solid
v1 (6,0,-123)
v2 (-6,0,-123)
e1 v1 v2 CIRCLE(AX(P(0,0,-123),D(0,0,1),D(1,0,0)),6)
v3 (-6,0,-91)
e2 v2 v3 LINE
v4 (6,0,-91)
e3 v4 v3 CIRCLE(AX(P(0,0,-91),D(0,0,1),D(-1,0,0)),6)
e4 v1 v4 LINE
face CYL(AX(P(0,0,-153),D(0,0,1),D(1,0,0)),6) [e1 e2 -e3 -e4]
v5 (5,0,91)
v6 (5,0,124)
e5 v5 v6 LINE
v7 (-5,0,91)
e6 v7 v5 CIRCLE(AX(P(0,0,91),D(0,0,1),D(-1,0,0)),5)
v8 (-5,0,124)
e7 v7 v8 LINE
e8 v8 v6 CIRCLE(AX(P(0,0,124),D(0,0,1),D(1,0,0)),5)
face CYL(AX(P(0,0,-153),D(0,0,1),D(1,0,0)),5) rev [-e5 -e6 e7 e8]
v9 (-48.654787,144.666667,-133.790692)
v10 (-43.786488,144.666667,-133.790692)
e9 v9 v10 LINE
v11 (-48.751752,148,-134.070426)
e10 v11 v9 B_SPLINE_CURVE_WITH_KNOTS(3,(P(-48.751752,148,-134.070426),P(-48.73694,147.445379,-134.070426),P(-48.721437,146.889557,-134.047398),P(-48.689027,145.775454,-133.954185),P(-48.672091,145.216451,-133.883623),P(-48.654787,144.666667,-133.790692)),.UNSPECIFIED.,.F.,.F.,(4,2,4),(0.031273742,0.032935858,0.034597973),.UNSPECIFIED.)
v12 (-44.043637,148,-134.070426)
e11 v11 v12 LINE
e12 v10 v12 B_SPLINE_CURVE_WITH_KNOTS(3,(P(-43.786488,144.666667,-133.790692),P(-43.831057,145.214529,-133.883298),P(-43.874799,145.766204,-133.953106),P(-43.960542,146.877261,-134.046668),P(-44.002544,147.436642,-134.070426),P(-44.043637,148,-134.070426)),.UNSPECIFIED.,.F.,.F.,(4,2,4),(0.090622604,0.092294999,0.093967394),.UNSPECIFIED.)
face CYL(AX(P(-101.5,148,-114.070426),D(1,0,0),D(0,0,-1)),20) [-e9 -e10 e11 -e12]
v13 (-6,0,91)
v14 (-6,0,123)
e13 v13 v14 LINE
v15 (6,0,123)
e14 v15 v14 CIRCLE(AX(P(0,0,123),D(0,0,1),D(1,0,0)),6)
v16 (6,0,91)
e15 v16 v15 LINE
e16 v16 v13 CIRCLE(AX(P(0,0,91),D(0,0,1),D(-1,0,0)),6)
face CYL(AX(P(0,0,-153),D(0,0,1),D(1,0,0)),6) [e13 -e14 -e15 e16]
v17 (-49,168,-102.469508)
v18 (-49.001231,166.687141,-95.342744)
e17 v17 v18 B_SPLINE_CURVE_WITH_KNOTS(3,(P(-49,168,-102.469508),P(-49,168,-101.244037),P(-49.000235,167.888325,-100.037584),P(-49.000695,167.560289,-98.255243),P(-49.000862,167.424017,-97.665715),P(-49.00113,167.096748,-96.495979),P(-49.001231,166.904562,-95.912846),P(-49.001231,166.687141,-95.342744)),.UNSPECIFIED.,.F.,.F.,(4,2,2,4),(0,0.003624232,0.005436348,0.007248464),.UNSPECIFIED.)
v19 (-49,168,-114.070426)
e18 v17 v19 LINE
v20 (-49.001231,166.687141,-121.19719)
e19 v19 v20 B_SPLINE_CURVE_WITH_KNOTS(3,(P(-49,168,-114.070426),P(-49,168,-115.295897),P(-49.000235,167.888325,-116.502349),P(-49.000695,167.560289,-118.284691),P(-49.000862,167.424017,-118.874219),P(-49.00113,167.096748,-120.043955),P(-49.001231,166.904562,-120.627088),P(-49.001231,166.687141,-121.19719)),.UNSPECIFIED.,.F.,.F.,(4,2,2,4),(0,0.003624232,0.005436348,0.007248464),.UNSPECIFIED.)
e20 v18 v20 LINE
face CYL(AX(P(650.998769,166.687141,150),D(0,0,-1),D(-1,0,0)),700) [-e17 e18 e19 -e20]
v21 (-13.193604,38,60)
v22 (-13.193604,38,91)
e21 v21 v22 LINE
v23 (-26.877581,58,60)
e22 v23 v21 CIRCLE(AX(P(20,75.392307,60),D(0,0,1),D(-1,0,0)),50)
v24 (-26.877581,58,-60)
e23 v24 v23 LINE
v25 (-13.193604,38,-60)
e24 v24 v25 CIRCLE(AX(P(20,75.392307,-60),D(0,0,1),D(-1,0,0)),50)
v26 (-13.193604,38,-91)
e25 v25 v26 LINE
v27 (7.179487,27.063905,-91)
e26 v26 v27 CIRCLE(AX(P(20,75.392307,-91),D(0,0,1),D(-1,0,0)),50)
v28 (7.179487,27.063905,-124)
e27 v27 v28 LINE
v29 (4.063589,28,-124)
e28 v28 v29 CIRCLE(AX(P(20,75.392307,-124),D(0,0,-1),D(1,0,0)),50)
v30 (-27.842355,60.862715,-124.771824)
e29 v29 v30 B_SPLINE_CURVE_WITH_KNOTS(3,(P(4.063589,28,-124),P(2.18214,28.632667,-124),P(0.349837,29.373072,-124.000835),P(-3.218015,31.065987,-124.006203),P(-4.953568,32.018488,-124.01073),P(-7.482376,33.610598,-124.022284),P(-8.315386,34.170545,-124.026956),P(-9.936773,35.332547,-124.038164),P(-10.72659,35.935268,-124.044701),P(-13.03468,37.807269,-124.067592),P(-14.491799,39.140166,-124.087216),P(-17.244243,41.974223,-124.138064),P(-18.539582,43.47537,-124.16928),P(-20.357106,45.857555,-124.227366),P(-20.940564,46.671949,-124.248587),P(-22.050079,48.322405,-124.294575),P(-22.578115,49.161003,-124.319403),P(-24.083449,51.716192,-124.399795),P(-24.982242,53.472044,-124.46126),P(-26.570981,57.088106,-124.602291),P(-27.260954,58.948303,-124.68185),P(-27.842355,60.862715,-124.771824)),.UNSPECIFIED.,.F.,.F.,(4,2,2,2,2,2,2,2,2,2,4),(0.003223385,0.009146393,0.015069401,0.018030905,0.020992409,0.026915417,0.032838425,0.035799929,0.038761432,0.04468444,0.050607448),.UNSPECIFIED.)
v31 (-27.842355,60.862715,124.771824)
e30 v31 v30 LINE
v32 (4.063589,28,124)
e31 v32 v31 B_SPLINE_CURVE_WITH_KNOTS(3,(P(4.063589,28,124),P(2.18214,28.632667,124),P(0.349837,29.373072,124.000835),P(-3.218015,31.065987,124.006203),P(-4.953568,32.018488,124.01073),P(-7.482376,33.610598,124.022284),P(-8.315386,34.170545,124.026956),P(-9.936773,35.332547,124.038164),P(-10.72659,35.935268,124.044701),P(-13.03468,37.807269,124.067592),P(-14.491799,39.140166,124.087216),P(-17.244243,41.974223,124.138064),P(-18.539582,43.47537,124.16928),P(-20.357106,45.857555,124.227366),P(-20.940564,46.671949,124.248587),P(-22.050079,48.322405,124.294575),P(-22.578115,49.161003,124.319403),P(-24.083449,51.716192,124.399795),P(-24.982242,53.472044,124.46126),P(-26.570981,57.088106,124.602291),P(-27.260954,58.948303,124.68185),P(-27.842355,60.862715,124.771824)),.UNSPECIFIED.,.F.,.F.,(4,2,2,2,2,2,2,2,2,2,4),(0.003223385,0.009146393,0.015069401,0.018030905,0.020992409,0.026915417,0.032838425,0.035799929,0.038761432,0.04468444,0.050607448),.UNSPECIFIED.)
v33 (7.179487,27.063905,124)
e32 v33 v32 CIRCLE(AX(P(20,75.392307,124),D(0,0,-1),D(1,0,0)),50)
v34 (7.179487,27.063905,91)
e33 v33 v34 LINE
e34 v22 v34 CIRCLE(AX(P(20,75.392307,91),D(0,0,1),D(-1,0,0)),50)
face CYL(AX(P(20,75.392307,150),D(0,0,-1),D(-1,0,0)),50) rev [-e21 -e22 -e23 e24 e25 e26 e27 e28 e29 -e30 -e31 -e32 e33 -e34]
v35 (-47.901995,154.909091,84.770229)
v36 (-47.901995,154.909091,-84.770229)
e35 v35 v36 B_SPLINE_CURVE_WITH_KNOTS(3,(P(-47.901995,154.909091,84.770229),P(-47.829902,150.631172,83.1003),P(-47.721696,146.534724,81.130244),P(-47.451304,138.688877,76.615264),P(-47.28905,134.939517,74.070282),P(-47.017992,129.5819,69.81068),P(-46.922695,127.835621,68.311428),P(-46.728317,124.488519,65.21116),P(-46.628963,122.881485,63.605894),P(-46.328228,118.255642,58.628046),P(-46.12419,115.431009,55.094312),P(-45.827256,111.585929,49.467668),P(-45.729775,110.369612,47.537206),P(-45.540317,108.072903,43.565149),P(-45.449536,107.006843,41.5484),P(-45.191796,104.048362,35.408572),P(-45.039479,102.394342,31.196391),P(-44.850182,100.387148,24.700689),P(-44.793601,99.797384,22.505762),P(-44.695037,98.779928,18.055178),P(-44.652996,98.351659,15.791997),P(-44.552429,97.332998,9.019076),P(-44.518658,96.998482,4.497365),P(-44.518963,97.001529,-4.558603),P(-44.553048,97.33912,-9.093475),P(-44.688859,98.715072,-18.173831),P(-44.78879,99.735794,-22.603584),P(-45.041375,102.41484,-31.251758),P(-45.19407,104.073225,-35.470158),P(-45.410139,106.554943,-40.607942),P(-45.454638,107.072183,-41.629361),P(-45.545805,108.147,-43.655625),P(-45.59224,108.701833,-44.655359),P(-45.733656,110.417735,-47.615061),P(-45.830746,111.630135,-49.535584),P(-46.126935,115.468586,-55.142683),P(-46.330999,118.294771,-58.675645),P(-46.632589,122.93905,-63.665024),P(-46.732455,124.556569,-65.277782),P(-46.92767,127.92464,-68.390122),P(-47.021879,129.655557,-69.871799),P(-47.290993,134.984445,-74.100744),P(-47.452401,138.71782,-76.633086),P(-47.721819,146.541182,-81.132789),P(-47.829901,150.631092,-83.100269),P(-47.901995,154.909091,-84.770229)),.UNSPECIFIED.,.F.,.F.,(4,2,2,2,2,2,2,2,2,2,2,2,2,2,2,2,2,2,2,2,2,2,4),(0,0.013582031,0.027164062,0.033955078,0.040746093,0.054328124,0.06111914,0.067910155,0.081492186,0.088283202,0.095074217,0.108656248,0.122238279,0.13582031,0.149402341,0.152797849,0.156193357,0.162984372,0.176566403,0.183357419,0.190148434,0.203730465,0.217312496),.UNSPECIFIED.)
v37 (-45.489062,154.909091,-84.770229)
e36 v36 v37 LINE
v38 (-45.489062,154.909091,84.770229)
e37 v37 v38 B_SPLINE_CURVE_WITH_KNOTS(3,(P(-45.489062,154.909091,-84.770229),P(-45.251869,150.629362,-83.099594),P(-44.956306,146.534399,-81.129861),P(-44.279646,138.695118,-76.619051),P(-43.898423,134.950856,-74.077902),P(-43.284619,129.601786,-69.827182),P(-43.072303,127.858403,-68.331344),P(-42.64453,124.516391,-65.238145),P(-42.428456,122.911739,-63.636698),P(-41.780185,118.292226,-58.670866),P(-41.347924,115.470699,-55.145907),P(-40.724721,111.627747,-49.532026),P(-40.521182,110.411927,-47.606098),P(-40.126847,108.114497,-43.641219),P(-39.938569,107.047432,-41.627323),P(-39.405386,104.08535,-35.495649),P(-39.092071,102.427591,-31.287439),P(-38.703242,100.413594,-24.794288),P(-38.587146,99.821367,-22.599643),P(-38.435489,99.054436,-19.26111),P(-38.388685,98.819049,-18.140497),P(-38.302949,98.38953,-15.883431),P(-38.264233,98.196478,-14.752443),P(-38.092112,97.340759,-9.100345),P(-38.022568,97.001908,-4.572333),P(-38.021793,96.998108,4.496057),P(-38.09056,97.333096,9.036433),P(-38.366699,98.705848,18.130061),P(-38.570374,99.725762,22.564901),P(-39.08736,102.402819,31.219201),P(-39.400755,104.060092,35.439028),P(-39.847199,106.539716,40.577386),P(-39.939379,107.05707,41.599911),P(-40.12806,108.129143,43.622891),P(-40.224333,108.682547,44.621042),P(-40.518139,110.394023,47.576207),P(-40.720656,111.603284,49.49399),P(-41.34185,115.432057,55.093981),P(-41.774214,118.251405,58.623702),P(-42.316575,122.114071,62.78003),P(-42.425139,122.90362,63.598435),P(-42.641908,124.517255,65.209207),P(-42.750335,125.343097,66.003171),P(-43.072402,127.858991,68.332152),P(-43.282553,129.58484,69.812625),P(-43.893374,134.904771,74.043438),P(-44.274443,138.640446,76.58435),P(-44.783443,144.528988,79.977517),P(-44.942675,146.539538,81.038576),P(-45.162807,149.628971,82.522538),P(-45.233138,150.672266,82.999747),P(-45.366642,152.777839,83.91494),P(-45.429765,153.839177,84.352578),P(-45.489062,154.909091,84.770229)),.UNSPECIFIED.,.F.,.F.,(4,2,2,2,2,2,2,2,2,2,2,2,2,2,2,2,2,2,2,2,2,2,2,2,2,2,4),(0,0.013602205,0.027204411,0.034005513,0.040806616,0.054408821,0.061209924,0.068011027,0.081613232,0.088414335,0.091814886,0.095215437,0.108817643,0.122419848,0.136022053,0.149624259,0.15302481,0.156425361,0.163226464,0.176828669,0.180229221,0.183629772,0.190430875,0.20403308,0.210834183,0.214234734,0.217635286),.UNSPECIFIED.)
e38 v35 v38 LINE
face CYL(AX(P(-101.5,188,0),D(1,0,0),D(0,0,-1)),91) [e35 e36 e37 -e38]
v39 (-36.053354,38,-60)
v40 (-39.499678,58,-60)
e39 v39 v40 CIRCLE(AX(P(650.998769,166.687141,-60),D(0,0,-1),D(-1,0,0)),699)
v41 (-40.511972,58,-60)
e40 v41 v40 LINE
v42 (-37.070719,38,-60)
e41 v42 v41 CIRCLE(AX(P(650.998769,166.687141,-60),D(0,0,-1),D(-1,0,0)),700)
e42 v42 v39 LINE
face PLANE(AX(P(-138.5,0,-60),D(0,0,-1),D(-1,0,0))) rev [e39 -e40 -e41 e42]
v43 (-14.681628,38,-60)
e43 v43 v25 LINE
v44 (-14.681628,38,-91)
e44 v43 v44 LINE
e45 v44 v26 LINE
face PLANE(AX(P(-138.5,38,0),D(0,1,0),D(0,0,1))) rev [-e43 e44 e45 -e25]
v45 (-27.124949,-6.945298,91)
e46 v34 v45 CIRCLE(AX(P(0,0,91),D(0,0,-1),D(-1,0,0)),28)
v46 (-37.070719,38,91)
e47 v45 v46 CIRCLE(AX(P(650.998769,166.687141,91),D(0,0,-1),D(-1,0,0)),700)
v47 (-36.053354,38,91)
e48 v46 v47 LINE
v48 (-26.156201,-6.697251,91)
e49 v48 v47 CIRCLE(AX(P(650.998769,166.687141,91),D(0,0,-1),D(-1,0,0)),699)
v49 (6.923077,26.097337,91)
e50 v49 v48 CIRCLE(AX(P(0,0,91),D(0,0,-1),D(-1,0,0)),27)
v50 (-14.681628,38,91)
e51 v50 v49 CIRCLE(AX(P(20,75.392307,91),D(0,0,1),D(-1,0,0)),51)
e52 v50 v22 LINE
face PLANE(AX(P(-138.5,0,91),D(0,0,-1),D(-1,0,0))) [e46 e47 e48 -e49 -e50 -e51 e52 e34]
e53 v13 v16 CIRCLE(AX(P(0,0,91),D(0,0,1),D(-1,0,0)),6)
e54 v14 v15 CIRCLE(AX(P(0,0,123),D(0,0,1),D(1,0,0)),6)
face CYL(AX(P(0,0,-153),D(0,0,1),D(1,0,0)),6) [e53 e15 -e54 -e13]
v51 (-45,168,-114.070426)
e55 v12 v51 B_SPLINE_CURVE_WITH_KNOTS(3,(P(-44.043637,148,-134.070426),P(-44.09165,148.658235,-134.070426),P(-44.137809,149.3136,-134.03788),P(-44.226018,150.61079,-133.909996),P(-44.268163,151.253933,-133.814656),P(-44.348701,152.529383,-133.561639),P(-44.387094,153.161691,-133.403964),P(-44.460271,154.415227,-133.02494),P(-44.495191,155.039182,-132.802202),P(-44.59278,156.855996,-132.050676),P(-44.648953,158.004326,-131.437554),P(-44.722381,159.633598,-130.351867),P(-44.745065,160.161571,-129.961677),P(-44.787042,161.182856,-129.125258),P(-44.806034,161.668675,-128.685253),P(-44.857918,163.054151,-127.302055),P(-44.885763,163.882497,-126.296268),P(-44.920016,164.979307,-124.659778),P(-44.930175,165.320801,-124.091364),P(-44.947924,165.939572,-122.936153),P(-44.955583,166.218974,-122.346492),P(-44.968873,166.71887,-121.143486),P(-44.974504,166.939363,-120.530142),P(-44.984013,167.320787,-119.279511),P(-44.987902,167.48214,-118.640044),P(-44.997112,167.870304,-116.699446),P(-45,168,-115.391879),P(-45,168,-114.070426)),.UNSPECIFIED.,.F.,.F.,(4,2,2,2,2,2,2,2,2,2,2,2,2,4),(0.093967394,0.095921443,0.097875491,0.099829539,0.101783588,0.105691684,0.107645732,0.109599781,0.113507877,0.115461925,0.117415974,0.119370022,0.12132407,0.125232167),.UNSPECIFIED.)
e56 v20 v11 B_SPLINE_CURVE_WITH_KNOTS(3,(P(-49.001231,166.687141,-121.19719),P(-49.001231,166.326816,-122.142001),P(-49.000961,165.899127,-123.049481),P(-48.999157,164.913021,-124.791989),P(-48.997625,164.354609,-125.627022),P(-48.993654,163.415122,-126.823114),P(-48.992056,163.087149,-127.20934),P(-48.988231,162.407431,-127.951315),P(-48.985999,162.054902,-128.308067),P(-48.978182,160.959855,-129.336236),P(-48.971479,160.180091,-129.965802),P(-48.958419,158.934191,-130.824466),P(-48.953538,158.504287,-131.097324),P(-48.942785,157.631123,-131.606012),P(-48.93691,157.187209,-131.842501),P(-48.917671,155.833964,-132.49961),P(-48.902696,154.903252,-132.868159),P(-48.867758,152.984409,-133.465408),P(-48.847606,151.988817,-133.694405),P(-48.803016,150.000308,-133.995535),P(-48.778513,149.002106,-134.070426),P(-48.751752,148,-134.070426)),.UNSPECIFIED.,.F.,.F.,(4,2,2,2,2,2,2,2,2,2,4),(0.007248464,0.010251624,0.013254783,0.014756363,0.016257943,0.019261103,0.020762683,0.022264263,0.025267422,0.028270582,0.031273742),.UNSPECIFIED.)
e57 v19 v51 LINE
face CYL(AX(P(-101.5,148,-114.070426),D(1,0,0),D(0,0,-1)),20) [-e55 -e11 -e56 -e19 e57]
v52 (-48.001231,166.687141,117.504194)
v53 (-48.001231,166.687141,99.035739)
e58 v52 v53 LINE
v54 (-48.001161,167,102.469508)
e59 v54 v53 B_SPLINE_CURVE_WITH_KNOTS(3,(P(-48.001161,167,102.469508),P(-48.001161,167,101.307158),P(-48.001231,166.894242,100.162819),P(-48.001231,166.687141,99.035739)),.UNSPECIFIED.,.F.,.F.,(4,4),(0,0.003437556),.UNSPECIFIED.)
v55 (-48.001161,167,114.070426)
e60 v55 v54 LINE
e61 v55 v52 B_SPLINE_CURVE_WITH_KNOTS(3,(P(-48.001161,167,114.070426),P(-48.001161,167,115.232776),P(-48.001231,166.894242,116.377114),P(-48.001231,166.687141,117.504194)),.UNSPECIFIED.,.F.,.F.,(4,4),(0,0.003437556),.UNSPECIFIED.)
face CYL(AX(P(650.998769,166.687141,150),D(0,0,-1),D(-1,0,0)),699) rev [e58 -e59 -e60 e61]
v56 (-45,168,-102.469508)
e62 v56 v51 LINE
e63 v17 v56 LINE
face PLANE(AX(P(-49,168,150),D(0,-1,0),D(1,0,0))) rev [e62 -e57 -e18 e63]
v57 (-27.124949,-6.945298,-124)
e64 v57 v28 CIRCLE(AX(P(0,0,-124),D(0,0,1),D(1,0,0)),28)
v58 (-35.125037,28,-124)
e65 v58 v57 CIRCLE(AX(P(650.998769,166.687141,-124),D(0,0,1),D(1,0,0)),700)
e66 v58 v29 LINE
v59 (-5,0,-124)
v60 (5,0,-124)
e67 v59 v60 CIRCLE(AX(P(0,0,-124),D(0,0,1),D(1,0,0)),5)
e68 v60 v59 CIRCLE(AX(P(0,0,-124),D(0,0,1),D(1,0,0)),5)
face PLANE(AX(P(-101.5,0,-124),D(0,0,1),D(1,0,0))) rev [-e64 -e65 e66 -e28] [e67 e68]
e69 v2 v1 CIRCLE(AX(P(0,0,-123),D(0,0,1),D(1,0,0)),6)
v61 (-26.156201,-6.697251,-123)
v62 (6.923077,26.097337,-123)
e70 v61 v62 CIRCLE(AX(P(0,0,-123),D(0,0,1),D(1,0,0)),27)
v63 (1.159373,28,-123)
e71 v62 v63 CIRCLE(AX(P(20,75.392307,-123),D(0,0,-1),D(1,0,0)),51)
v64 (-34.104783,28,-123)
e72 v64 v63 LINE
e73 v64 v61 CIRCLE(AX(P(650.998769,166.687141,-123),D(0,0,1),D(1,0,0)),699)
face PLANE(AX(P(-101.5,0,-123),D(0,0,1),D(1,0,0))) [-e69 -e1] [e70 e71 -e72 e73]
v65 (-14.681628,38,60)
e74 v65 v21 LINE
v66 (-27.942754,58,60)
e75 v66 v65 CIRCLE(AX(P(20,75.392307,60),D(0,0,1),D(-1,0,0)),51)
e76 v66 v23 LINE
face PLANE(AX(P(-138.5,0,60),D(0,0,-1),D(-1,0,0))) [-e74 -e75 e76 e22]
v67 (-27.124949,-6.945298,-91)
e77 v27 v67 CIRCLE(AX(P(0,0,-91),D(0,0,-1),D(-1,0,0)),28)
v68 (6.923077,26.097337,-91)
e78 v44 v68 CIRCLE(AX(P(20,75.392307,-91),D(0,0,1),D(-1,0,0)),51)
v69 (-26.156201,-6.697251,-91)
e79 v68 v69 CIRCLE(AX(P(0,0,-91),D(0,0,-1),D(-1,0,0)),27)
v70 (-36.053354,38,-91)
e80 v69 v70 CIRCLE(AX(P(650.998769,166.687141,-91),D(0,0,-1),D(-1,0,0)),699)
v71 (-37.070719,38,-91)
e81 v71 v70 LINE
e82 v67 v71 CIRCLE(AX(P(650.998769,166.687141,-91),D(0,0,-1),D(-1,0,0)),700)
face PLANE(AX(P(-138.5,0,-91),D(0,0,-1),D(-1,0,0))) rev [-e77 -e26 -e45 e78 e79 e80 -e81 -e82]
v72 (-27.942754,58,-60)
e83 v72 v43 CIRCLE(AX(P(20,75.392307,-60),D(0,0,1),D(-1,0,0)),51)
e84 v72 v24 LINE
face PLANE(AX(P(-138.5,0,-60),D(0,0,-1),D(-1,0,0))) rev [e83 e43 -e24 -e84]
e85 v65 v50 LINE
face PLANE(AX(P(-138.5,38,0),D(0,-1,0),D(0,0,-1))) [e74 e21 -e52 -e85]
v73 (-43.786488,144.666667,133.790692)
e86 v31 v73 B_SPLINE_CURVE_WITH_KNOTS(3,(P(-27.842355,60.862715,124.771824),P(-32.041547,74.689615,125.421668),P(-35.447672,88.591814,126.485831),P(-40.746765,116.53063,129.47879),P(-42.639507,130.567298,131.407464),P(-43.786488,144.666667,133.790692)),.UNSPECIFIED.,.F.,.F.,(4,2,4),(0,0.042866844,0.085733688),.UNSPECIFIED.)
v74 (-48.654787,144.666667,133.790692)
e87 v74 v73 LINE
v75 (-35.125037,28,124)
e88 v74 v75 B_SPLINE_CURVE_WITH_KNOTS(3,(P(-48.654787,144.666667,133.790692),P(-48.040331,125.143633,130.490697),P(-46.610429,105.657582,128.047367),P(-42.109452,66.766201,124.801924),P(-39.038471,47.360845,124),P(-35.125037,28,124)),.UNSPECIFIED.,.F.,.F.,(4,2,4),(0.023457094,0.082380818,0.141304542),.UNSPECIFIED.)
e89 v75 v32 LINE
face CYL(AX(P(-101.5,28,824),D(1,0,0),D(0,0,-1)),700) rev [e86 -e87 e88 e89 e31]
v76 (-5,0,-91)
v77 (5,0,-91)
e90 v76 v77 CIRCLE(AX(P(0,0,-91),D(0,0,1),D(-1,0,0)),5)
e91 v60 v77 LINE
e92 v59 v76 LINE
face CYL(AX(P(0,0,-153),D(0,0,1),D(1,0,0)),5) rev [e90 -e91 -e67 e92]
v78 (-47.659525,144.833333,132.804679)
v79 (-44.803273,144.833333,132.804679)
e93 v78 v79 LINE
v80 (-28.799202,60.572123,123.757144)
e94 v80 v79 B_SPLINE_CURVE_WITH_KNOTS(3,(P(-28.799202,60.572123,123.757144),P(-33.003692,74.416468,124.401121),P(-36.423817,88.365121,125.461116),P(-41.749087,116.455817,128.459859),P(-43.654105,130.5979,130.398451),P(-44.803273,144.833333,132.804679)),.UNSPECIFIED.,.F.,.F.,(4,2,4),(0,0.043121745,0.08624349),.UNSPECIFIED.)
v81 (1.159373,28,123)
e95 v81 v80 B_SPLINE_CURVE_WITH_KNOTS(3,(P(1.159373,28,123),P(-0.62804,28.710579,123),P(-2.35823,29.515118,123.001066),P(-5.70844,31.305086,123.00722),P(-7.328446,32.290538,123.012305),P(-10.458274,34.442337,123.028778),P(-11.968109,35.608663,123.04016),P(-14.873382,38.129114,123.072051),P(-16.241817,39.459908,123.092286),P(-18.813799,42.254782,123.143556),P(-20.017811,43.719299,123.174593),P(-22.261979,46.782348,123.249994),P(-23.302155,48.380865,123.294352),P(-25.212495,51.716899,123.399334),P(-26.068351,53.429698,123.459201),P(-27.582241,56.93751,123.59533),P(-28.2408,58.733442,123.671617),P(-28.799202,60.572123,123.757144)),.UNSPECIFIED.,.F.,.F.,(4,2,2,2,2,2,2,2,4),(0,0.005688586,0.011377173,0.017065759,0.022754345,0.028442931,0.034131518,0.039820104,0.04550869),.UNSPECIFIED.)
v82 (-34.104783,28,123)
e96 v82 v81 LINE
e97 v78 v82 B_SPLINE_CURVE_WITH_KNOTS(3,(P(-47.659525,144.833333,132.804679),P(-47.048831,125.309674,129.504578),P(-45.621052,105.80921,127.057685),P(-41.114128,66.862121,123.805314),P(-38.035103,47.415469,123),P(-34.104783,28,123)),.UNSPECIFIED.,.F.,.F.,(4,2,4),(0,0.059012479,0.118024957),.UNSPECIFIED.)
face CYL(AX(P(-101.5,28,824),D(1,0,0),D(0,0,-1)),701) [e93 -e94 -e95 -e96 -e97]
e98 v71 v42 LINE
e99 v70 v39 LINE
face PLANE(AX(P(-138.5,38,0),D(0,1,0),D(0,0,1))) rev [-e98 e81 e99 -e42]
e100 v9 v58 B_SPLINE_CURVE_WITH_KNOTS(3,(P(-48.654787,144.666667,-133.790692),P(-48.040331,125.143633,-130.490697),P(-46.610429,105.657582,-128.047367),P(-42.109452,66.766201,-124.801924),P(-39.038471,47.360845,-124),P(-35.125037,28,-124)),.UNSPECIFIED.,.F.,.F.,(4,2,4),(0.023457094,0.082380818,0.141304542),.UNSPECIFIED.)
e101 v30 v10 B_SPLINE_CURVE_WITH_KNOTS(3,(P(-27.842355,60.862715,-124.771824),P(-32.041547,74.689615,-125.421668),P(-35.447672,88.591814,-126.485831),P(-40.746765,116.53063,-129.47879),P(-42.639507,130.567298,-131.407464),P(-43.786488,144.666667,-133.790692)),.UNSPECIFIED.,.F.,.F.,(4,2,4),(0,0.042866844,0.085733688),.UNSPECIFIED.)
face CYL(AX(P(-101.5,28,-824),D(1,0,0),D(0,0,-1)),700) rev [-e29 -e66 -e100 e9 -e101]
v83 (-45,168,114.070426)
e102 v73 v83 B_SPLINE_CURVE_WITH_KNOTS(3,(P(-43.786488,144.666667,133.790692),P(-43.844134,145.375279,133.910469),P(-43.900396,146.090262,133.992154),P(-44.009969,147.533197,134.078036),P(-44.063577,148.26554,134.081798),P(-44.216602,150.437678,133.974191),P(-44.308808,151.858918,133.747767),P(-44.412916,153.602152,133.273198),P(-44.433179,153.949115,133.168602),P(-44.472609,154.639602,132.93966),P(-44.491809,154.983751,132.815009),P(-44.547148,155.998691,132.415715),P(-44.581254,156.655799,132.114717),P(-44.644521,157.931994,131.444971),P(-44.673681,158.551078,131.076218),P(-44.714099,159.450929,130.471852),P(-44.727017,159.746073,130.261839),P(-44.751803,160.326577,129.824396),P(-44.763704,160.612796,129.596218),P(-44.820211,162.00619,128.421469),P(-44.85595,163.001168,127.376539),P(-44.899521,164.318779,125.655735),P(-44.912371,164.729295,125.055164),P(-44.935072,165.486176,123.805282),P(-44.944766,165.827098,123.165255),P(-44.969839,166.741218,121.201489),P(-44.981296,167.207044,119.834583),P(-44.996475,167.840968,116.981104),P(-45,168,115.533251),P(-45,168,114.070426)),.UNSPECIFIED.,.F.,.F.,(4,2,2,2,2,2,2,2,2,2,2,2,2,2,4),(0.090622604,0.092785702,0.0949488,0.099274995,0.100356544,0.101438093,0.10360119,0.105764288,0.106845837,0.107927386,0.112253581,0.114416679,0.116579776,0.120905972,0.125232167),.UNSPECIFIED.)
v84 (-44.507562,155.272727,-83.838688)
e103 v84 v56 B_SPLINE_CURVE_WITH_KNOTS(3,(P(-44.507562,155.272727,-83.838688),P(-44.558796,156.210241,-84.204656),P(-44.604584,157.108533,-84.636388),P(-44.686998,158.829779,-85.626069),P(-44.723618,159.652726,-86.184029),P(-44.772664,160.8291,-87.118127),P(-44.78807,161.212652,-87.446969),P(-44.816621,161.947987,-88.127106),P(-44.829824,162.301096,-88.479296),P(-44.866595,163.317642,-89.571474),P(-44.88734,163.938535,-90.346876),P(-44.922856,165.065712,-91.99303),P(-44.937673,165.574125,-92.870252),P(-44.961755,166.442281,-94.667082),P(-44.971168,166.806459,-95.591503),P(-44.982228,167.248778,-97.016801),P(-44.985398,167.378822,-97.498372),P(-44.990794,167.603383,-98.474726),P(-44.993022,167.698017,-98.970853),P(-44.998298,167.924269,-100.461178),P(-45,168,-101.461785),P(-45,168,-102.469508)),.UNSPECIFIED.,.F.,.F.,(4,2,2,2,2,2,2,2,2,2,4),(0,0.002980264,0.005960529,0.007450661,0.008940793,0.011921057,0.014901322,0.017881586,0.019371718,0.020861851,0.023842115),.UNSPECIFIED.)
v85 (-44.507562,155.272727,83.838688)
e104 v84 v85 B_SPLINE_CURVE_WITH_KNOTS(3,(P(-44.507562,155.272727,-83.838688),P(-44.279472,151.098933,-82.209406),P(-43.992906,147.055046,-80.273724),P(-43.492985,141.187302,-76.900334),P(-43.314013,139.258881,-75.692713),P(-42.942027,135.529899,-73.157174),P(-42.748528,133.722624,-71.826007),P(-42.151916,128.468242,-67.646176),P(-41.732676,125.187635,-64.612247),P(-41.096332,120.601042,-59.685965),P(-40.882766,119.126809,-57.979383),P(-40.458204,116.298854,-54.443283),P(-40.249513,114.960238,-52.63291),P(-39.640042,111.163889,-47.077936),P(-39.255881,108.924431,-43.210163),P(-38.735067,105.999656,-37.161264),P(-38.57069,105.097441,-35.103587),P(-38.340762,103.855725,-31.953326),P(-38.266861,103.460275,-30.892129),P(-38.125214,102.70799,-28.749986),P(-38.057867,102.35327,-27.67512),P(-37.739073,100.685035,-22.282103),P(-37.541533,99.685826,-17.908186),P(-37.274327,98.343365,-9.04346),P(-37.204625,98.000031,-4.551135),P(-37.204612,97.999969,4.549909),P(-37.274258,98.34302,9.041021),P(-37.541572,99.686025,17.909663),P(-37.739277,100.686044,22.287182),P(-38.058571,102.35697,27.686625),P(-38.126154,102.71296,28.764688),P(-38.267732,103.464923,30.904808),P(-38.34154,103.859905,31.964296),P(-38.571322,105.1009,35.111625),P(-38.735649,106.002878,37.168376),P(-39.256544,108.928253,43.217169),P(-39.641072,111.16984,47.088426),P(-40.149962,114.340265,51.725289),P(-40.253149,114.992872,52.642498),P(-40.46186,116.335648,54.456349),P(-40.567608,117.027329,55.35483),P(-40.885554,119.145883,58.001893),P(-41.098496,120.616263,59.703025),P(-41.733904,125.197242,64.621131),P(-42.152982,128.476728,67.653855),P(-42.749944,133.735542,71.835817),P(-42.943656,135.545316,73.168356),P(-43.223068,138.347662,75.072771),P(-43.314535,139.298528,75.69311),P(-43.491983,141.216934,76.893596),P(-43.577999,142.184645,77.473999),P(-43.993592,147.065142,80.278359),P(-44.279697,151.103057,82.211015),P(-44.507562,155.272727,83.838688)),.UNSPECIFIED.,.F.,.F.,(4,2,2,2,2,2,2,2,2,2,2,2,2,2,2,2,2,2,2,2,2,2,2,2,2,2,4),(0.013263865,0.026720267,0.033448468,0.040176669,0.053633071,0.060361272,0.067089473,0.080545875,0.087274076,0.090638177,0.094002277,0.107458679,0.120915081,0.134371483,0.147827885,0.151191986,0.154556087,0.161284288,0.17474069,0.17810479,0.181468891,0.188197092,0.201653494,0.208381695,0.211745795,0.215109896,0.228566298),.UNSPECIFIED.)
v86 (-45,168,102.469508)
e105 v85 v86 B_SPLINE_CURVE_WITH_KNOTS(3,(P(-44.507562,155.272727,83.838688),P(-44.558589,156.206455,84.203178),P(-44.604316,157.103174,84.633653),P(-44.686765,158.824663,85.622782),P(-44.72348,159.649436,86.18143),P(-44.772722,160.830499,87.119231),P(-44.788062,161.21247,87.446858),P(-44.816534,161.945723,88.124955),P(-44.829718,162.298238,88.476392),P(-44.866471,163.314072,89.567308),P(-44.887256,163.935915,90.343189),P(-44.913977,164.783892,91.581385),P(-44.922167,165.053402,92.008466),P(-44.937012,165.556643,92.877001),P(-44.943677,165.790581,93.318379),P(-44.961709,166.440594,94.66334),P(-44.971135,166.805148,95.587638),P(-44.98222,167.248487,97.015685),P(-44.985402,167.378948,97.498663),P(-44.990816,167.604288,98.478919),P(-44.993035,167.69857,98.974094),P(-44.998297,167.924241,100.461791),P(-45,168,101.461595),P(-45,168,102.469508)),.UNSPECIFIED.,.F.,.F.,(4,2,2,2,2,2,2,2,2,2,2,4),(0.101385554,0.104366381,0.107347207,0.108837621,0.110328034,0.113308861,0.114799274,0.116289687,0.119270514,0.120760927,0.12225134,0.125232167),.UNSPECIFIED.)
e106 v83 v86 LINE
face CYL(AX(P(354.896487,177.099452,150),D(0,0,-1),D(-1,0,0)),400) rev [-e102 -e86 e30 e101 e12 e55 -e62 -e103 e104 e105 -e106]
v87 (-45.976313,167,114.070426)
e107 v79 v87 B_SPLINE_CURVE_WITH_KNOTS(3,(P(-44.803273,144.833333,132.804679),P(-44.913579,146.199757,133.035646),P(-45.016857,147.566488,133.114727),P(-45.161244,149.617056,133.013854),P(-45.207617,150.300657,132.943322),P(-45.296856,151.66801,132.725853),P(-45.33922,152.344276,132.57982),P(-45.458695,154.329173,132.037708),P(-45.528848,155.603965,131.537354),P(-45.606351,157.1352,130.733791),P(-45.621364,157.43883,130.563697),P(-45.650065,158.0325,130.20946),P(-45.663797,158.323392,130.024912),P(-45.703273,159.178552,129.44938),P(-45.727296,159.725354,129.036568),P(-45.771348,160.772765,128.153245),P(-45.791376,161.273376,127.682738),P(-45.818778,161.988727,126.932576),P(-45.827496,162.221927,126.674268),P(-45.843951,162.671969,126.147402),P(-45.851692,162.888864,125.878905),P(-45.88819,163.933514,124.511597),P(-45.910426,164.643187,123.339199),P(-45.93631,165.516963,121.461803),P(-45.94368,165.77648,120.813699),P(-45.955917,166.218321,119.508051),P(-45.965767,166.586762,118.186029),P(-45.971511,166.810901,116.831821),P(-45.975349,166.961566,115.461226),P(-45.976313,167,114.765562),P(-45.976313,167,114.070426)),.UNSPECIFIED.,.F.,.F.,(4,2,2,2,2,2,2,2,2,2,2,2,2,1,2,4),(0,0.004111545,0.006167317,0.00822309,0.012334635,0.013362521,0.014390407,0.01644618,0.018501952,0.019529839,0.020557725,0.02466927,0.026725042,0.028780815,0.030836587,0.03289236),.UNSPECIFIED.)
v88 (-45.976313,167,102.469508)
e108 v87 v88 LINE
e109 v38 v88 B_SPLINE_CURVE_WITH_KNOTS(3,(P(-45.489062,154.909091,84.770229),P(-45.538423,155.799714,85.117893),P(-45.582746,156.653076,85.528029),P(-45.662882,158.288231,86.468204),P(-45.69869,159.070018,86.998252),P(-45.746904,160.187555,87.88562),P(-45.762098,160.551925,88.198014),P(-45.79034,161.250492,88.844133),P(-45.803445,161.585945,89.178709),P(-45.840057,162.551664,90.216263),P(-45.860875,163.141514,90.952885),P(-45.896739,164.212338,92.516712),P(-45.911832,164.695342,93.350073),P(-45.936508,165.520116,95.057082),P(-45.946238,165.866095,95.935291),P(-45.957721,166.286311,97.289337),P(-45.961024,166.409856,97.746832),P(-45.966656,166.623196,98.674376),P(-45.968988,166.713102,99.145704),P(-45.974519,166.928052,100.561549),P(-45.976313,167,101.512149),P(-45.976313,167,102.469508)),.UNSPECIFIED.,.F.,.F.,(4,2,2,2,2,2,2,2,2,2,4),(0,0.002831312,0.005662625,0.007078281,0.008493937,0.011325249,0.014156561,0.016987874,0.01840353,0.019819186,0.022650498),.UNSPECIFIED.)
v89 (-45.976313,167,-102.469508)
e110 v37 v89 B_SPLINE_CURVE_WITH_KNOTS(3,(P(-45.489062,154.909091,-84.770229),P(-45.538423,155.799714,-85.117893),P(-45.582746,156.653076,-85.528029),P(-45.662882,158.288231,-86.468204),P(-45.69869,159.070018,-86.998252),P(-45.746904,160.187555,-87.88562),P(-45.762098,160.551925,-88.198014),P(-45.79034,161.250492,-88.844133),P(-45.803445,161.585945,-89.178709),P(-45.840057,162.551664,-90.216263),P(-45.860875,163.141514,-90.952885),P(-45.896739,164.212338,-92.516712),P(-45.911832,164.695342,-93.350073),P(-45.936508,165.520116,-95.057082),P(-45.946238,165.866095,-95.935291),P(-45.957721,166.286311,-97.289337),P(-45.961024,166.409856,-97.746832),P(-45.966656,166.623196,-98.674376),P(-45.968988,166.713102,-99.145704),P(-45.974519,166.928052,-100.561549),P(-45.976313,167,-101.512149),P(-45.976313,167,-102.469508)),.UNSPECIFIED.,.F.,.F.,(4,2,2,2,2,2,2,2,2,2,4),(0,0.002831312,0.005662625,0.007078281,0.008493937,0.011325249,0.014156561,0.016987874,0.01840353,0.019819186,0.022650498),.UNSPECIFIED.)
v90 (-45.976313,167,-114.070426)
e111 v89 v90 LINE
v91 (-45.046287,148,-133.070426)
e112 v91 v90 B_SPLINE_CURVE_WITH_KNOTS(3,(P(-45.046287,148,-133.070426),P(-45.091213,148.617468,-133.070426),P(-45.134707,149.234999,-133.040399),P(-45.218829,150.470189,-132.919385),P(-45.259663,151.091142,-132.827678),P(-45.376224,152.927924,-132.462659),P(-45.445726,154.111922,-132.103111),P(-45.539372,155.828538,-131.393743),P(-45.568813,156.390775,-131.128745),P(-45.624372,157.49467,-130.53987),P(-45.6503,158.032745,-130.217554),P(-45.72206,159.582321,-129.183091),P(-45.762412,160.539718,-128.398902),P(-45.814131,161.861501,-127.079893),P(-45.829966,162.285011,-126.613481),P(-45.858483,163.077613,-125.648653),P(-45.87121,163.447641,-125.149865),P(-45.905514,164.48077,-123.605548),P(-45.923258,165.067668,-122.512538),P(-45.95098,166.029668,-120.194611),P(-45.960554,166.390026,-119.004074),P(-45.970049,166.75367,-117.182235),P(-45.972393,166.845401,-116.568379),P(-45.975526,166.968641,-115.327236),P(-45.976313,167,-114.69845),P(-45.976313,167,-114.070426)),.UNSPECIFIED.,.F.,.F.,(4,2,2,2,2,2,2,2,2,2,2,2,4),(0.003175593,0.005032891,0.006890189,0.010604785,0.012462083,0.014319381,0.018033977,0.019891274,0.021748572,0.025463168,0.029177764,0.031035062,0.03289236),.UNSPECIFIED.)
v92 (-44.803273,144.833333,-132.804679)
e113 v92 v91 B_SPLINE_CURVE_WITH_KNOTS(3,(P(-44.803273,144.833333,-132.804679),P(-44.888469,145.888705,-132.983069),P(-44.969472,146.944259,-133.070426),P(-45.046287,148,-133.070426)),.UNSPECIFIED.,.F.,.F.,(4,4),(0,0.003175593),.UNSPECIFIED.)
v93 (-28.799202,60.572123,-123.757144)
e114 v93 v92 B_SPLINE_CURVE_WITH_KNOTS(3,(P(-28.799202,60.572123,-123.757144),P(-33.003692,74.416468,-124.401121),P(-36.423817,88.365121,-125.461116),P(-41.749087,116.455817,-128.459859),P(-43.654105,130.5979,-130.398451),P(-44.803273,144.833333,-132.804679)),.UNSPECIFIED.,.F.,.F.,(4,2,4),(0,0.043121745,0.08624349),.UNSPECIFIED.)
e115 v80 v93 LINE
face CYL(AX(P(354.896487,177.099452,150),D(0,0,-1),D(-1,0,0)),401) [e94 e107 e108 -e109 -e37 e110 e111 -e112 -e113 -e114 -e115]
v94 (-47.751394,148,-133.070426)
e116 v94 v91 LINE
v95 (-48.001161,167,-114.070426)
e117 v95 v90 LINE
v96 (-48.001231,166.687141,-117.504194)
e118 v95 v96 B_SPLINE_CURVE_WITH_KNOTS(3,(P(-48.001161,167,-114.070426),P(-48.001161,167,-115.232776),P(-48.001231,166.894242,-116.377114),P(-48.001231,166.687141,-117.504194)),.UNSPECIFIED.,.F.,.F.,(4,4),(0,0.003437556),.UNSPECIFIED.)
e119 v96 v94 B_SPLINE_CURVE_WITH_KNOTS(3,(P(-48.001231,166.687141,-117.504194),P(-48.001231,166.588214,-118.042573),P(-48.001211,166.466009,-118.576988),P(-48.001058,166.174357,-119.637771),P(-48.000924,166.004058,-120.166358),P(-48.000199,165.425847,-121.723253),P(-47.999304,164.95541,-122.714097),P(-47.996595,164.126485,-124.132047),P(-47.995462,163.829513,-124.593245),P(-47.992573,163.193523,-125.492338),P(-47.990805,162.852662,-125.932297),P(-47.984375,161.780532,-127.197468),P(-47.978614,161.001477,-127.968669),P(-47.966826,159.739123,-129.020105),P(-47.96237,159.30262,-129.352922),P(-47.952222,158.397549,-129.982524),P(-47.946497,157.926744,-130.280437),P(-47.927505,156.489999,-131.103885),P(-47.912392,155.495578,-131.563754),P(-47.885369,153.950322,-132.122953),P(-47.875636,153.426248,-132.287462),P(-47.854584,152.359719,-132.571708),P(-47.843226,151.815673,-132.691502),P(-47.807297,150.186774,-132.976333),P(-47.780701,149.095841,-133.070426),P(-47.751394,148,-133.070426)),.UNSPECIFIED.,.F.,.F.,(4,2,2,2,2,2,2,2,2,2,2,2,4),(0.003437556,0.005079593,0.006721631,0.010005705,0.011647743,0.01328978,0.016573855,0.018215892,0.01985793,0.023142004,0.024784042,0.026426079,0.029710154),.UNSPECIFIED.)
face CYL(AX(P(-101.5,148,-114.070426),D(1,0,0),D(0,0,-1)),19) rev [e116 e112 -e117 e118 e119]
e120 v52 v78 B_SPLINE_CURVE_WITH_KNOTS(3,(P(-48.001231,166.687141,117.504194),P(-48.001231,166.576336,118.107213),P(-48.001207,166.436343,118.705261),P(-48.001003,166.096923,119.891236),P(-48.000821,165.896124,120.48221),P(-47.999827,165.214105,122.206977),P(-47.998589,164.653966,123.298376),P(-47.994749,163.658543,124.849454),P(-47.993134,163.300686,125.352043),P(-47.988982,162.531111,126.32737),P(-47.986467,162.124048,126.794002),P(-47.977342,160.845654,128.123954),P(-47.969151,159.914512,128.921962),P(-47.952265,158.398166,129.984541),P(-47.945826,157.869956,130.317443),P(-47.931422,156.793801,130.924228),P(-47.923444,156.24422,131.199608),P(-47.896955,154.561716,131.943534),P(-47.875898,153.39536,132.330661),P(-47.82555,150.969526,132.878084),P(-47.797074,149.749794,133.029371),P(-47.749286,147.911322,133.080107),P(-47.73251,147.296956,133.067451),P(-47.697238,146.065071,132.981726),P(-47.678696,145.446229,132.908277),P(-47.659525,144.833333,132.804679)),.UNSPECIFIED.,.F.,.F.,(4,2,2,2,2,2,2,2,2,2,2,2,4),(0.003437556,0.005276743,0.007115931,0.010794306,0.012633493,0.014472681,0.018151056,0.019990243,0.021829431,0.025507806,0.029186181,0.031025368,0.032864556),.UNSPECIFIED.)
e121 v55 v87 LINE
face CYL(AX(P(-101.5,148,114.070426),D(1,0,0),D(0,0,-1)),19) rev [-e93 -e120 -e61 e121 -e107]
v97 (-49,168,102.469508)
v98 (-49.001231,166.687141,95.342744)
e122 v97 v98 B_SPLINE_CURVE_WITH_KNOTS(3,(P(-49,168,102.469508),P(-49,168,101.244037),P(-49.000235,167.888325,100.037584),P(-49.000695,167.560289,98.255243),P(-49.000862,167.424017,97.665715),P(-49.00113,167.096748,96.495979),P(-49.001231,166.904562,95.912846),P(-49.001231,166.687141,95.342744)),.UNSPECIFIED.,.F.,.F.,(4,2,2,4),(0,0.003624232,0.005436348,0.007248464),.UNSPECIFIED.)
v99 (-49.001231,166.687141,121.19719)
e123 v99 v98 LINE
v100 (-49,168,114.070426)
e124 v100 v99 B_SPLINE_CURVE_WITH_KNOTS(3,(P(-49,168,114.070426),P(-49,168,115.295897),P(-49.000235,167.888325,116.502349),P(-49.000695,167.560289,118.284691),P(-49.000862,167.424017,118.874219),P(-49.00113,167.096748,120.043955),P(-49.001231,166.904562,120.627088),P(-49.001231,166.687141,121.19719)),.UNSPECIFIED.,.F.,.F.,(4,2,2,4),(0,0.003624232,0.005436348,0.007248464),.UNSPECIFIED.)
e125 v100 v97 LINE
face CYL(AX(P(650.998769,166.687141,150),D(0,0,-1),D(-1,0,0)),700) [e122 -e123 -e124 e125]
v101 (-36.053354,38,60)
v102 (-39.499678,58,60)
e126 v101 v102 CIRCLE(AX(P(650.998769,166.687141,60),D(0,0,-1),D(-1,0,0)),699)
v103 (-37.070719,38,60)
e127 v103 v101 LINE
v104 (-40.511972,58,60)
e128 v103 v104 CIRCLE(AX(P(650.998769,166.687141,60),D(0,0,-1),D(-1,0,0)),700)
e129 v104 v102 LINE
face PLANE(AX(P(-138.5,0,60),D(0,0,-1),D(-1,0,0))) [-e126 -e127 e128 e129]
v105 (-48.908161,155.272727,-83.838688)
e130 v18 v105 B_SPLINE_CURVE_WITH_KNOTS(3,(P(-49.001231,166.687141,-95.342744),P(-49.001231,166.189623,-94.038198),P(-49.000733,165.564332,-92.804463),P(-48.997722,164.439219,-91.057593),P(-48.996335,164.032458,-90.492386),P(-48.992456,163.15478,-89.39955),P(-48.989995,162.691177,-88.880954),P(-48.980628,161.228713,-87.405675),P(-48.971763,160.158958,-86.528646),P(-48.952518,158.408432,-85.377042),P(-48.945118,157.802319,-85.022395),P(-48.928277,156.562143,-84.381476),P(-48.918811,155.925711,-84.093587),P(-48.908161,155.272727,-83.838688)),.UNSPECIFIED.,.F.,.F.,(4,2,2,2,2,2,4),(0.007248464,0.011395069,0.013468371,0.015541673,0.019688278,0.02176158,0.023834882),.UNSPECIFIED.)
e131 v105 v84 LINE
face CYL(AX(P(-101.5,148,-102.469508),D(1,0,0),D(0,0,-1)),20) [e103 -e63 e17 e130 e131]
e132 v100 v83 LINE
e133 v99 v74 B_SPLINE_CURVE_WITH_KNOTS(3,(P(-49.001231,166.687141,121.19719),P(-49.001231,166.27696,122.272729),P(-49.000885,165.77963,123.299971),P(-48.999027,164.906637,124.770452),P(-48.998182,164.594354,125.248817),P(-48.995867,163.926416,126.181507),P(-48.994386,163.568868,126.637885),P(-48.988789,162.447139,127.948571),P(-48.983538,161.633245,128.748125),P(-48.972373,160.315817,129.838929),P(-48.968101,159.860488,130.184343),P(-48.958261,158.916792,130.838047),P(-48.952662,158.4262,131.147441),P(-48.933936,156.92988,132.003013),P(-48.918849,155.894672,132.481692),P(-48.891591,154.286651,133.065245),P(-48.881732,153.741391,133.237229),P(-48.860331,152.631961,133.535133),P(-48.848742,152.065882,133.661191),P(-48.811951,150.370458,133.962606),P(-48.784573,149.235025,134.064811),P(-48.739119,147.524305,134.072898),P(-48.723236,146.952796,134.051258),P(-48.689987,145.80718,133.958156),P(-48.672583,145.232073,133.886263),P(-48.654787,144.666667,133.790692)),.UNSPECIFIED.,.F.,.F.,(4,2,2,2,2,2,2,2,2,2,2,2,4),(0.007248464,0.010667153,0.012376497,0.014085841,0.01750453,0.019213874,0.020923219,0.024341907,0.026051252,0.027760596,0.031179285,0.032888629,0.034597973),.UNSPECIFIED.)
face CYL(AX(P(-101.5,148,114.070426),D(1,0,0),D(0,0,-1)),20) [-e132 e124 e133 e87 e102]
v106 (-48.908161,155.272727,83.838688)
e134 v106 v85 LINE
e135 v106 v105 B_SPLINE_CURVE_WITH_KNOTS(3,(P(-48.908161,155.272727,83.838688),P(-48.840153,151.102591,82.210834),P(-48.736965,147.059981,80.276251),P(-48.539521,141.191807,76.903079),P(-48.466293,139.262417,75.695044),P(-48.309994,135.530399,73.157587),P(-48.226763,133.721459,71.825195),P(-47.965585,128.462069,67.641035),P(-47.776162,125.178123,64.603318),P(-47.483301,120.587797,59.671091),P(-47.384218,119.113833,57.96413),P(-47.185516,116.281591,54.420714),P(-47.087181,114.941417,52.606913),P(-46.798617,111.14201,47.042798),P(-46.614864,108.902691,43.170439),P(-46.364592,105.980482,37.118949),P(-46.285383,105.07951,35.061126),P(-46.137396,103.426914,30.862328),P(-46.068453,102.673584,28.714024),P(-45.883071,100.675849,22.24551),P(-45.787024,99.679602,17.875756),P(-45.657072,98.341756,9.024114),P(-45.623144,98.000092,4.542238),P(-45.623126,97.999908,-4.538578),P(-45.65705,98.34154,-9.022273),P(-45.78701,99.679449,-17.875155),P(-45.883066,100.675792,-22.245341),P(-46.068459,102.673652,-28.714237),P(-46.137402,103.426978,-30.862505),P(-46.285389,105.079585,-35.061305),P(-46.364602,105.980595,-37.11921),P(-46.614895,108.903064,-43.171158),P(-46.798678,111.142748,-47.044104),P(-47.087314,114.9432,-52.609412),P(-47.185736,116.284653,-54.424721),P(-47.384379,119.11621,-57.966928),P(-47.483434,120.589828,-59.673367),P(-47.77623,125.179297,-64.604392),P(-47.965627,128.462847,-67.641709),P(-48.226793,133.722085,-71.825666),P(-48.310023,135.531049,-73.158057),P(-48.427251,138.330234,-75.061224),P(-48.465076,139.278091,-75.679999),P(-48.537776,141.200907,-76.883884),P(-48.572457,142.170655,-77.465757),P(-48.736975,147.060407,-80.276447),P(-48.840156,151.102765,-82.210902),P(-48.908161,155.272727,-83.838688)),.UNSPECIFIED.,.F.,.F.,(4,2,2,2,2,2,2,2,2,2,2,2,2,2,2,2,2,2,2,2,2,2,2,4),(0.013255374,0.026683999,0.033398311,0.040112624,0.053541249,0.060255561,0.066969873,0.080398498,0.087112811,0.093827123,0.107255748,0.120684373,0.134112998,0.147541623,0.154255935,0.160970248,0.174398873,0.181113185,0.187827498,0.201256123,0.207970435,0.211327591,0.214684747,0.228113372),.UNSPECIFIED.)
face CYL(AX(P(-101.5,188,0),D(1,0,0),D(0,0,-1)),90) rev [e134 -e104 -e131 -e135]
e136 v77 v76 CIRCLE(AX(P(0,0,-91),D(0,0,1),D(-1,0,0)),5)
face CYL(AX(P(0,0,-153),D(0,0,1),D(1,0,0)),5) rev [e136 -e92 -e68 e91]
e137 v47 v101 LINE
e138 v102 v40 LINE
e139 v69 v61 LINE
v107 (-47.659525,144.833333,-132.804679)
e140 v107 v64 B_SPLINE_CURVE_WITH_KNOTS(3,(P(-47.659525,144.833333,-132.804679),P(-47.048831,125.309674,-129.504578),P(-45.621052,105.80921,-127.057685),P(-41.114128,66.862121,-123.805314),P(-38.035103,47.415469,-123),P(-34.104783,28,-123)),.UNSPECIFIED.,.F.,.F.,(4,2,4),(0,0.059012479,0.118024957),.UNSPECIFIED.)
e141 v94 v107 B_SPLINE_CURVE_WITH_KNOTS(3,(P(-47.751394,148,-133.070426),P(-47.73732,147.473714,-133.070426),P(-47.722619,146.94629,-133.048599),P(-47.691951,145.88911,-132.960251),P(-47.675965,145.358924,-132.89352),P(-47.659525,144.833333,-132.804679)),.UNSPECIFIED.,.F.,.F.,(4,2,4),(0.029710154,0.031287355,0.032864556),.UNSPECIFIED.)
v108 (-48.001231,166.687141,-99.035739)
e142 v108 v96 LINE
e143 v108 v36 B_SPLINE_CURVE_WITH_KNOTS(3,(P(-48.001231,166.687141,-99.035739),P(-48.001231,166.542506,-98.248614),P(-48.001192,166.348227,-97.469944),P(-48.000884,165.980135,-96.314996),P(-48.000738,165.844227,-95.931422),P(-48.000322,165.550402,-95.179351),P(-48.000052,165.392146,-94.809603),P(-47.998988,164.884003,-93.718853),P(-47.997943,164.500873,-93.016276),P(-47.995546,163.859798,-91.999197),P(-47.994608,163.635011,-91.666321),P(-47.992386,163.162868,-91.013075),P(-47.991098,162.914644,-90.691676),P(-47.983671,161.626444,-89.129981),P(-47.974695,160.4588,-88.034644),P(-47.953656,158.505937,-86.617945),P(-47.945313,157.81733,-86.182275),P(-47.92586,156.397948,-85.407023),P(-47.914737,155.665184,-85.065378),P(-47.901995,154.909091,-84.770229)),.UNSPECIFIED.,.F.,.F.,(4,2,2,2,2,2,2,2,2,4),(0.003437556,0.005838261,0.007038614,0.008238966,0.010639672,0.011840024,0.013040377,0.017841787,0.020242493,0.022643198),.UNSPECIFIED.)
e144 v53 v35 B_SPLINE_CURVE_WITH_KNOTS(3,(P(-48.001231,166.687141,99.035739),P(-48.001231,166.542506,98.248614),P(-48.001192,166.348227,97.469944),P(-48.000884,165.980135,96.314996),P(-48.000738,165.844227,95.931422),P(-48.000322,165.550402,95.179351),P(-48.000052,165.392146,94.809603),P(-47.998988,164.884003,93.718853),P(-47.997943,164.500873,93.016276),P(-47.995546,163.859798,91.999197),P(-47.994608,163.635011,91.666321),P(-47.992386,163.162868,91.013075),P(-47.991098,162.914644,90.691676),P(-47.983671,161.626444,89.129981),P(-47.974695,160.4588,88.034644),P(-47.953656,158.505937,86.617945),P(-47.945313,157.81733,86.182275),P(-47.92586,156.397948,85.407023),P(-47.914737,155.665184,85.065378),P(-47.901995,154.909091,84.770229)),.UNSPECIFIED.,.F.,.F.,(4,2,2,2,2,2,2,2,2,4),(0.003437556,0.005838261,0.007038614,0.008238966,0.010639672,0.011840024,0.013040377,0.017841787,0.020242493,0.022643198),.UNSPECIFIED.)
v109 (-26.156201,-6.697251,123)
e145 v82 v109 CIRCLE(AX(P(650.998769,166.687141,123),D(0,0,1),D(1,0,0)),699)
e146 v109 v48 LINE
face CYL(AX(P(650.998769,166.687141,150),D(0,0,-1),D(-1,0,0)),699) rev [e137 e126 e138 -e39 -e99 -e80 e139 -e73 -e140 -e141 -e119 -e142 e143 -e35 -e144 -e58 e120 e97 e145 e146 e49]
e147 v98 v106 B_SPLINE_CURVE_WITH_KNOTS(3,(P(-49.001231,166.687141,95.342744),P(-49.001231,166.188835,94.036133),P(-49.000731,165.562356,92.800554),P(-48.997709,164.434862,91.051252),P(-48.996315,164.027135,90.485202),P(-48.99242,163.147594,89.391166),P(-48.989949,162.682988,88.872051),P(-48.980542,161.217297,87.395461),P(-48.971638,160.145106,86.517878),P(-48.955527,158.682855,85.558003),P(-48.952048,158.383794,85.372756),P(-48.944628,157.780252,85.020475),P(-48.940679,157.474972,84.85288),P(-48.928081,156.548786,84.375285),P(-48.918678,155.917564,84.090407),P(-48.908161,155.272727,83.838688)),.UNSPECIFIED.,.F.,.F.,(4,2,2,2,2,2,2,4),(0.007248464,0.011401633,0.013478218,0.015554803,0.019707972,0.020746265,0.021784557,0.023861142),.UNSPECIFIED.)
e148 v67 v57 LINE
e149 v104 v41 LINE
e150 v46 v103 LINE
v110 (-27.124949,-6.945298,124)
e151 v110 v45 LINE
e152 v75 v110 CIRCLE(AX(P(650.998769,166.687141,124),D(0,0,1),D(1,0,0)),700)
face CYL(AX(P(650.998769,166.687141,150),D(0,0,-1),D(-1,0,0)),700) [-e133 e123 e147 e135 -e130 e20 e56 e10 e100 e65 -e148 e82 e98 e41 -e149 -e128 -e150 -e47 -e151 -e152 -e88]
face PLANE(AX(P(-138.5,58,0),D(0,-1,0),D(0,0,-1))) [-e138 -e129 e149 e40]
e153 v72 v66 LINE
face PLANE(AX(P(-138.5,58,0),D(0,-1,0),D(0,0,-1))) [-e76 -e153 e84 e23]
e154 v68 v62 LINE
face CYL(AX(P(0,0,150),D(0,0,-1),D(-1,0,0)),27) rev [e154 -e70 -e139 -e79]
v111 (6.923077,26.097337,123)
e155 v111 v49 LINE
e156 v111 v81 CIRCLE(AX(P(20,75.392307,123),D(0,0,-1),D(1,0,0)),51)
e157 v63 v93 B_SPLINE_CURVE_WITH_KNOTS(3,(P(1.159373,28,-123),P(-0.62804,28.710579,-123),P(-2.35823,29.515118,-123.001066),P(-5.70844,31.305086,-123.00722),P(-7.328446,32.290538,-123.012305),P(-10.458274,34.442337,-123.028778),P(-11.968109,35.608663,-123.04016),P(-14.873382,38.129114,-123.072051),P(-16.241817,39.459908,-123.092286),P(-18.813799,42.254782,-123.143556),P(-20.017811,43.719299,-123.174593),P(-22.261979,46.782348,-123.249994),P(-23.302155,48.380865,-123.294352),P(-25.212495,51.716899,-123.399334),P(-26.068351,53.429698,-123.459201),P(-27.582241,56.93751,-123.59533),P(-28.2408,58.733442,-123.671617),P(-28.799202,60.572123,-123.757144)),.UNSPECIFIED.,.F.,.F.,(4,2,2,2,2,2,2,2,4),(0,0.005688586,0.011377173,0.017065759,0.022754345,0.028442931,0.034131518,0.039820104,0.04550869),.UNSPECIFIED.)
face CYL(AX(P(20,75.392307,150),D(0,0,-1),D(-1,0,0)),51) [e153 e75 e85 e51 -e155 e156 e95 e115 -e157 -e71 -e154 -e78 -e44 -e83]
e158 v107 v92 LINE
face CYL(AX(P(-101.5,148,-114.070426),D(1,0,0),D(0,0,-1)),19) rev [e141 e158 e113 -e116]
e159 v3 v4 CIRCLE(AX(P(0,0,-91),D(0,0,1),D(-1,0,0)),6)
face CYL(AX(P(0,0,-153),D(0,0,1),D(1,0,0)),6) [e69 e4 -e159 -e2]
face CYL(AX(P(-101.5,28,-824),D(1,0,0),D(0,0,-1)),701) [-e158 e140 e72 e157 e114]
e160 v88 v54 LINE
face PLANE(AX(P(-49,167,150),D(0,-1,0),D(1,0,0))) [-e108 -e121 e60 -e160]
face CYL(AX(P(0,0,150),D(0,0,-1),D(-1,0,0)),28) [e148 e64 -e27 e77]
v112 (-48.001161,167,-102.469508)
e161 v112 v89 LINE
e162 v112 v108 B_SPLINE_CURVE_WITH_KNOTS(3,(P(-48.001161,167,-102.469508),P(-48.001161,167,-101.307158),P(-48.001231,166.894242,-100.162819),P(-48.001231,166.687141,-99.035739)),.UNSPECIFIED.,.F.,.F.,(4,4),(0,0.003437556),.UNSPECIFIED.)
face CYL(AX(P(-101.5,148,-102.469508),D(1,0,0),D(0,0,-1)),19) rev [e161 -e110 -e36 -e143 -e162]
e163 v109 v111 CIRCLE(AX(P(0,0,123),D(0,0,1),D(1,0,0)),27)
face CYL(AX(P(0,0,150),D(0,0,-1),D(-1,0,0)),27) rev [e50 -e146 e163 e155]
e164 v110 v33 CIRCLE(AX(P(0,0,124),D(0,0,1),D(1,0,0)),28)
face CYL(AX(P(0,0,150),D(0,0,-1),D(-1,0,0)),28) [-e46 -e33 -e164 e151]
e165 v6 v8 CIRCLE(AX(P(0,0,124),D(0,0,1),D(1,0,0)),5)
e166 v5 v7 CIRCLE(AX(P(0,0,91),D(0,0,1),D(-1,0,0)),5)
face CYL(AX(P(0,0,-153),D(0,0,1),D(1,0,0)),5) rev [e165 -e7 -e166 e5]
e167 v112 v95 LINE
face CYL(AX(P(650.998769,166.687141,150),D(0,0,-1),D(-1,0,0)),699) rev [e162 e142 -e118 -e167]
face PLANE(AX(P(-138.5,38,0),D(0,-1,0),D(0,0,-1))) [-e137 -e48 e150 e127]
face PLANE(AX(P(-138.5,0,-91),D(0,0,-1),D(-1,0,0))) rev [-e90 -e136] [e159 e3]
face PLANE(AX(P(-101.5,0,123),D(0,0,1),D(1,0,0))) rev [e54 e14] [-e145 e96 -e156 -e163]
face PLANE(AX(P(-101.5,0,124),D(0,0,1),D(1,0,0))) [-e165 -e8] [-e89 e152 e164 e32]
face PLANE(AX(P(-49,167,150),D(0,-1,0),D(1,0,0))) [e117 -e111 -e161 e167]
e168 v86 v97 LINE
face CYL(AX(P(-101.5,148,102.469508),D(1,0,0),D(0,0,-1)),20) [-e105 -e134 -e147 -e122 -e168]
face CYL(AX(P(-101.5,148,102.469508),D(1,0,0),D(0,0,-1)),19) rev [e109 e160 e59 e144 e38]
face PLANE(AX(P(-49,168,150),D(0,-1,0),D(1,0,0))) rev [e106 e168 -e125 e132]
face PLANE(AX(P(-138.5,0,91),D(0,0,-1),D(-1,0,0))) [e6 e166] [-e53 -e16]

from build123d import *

# Parameters (mm, degrees)
BOSS_EXTRUDE1_DEPTH = 150
CUT_EXTRUDE5_DEPTH  = 101.5
SKETCH3_R           = 5
CUT_EXTRUDE6_DEPTH  = 277
CUT_EXTRUDE8_DEPTH  = 138.5
SHELL1_T            = -1


with BuildPart() as part:
    # Sketch1 → Boss-Extrude1 (new, symmetric)
    with BuildSketch(Plane.XY):
        with BuildLine():
            Line((-49, 168), (-45, 168))
            ThreePointArc((-45, 168), (-40.070744665, 113.846892769), (-27.842355225, 60.862715201))
            ThreePointArc((-27.842355225, 60.862715201), (-14.721546329, 39.414338757), (7.179487179, 27.063905185))
            ThreePointArc((7.179487179, 27.063905185), (19.713239873, -19.884370086), (-27.124948702, -6.945297538))
            ThreePointArc((-27.124948702, -6.945297538), (-43.592377915, 79.835895525), (-49, 168))
        make_face()
    extrude(amount=BOSS_EXTRUDE1_DEPTH, both=True)

    # Sketch2 → Cut-Extrude5 (cut, symmetric)
    with BuildSketch(Plane(origin=(0, 0, 0), x_dir=(0, 0, -1), z_dir=(1, 0, 0))):
        with BuildLine():
            ThreePointArc((-133.790691972, 144.666666667), (-129.345678345, 160.909944487), (-114.070426028, 168))
            Line((-114.070426028, 168), (-150, 168))
            Line((-150, 168), (-150, -28))
            Line((-150, -28), (-124, -28))
            Line((-124, -28), (-124, -8))
            Line((-124, -8), (-124, 28))
            ThreePointArc((-124, 28), (-126.451967382, 86.538382196), (-133.790691972, 144.666666667))
        make_face()
        with BuildLine():
            Line((102.46950766, 168), (-102.46950766, 168))
            ThreePointArc((-102.46950766, 168), (-91.187986163, 164.514456477), (-83.838688085, 155.272727273))
            ThreePointArc((-83.838688085, 155.272727273), (0, 98), (83.838688085, 155.272727273))
            ThreePointArc((83.838688085, 155.272727273), (91.187986163, 164.514456477), (102.46950766, 168))
        make_face()
        with BuildLine():
            Line((150, 168), (114.070426028, 168))
            ThreePointArc((114.070426028, 168), (129.345678345, 160.909944487), (133.790691972, 144.666666667))
            ThreePointArc((133.790691972, 144.666666667), (126.451967382, 86.538382196), (124, 28))
            Line((124, 28), (124, -8))
            Line((124, -8), (124, -28))
            Line((124, -28), (150, -28))
            Line((150, -28), (150, 168))
        make_face()
    extrude(amount=CUT_EXTRUDE5_DEPTH, both=True, mode=Mode.SUBTRACT)

    # Sketch3 → Cut-Extrude6 (cut)
    with BuildSketch(Plane.XY.offset(124)):
        Circle(SKETCH3_R)
    extrude(amount=-CUT_EXTRUDE6_DEPTH, mode=Mode.SUBTRACT)

    # Sketch4 → Cut-Extrude8 (cut, symmetric)
    with BuildSketch(Plane(origin=(0, 0, 0), x_dir=(0, 0, -1), z_dir=(1, 0, 0))):
        Polygon((-91, -28), (-91, 38), (-60, 38), (-60, 58), (60, 58), (60, 38), (91, 38), (91, -28), align=None)
    extrude(amount=CUT_EXTRUDE8_DEPTH, both=True, mode=Mode.SUBTRACT)

    # Shell1
    shell1_openings = [part.faces().sort_by_distance(p)[0] for p in [
        (-25.132161433, 38, 75.5),
        (-29.63441401, 47.053048744, 60),
        (-33.694776993, 58, 0),
        (-29.63441401, 47.053048744, -60),
        (-25.132161433, 38, -75.5),
        (-4.519844727, 5.226646447, 91),
        (-4.519844727, 5.226646447, -91),
    ]]
    offset(amount=SHELL1_T, openings=shell1_openings)


solid = part.part
